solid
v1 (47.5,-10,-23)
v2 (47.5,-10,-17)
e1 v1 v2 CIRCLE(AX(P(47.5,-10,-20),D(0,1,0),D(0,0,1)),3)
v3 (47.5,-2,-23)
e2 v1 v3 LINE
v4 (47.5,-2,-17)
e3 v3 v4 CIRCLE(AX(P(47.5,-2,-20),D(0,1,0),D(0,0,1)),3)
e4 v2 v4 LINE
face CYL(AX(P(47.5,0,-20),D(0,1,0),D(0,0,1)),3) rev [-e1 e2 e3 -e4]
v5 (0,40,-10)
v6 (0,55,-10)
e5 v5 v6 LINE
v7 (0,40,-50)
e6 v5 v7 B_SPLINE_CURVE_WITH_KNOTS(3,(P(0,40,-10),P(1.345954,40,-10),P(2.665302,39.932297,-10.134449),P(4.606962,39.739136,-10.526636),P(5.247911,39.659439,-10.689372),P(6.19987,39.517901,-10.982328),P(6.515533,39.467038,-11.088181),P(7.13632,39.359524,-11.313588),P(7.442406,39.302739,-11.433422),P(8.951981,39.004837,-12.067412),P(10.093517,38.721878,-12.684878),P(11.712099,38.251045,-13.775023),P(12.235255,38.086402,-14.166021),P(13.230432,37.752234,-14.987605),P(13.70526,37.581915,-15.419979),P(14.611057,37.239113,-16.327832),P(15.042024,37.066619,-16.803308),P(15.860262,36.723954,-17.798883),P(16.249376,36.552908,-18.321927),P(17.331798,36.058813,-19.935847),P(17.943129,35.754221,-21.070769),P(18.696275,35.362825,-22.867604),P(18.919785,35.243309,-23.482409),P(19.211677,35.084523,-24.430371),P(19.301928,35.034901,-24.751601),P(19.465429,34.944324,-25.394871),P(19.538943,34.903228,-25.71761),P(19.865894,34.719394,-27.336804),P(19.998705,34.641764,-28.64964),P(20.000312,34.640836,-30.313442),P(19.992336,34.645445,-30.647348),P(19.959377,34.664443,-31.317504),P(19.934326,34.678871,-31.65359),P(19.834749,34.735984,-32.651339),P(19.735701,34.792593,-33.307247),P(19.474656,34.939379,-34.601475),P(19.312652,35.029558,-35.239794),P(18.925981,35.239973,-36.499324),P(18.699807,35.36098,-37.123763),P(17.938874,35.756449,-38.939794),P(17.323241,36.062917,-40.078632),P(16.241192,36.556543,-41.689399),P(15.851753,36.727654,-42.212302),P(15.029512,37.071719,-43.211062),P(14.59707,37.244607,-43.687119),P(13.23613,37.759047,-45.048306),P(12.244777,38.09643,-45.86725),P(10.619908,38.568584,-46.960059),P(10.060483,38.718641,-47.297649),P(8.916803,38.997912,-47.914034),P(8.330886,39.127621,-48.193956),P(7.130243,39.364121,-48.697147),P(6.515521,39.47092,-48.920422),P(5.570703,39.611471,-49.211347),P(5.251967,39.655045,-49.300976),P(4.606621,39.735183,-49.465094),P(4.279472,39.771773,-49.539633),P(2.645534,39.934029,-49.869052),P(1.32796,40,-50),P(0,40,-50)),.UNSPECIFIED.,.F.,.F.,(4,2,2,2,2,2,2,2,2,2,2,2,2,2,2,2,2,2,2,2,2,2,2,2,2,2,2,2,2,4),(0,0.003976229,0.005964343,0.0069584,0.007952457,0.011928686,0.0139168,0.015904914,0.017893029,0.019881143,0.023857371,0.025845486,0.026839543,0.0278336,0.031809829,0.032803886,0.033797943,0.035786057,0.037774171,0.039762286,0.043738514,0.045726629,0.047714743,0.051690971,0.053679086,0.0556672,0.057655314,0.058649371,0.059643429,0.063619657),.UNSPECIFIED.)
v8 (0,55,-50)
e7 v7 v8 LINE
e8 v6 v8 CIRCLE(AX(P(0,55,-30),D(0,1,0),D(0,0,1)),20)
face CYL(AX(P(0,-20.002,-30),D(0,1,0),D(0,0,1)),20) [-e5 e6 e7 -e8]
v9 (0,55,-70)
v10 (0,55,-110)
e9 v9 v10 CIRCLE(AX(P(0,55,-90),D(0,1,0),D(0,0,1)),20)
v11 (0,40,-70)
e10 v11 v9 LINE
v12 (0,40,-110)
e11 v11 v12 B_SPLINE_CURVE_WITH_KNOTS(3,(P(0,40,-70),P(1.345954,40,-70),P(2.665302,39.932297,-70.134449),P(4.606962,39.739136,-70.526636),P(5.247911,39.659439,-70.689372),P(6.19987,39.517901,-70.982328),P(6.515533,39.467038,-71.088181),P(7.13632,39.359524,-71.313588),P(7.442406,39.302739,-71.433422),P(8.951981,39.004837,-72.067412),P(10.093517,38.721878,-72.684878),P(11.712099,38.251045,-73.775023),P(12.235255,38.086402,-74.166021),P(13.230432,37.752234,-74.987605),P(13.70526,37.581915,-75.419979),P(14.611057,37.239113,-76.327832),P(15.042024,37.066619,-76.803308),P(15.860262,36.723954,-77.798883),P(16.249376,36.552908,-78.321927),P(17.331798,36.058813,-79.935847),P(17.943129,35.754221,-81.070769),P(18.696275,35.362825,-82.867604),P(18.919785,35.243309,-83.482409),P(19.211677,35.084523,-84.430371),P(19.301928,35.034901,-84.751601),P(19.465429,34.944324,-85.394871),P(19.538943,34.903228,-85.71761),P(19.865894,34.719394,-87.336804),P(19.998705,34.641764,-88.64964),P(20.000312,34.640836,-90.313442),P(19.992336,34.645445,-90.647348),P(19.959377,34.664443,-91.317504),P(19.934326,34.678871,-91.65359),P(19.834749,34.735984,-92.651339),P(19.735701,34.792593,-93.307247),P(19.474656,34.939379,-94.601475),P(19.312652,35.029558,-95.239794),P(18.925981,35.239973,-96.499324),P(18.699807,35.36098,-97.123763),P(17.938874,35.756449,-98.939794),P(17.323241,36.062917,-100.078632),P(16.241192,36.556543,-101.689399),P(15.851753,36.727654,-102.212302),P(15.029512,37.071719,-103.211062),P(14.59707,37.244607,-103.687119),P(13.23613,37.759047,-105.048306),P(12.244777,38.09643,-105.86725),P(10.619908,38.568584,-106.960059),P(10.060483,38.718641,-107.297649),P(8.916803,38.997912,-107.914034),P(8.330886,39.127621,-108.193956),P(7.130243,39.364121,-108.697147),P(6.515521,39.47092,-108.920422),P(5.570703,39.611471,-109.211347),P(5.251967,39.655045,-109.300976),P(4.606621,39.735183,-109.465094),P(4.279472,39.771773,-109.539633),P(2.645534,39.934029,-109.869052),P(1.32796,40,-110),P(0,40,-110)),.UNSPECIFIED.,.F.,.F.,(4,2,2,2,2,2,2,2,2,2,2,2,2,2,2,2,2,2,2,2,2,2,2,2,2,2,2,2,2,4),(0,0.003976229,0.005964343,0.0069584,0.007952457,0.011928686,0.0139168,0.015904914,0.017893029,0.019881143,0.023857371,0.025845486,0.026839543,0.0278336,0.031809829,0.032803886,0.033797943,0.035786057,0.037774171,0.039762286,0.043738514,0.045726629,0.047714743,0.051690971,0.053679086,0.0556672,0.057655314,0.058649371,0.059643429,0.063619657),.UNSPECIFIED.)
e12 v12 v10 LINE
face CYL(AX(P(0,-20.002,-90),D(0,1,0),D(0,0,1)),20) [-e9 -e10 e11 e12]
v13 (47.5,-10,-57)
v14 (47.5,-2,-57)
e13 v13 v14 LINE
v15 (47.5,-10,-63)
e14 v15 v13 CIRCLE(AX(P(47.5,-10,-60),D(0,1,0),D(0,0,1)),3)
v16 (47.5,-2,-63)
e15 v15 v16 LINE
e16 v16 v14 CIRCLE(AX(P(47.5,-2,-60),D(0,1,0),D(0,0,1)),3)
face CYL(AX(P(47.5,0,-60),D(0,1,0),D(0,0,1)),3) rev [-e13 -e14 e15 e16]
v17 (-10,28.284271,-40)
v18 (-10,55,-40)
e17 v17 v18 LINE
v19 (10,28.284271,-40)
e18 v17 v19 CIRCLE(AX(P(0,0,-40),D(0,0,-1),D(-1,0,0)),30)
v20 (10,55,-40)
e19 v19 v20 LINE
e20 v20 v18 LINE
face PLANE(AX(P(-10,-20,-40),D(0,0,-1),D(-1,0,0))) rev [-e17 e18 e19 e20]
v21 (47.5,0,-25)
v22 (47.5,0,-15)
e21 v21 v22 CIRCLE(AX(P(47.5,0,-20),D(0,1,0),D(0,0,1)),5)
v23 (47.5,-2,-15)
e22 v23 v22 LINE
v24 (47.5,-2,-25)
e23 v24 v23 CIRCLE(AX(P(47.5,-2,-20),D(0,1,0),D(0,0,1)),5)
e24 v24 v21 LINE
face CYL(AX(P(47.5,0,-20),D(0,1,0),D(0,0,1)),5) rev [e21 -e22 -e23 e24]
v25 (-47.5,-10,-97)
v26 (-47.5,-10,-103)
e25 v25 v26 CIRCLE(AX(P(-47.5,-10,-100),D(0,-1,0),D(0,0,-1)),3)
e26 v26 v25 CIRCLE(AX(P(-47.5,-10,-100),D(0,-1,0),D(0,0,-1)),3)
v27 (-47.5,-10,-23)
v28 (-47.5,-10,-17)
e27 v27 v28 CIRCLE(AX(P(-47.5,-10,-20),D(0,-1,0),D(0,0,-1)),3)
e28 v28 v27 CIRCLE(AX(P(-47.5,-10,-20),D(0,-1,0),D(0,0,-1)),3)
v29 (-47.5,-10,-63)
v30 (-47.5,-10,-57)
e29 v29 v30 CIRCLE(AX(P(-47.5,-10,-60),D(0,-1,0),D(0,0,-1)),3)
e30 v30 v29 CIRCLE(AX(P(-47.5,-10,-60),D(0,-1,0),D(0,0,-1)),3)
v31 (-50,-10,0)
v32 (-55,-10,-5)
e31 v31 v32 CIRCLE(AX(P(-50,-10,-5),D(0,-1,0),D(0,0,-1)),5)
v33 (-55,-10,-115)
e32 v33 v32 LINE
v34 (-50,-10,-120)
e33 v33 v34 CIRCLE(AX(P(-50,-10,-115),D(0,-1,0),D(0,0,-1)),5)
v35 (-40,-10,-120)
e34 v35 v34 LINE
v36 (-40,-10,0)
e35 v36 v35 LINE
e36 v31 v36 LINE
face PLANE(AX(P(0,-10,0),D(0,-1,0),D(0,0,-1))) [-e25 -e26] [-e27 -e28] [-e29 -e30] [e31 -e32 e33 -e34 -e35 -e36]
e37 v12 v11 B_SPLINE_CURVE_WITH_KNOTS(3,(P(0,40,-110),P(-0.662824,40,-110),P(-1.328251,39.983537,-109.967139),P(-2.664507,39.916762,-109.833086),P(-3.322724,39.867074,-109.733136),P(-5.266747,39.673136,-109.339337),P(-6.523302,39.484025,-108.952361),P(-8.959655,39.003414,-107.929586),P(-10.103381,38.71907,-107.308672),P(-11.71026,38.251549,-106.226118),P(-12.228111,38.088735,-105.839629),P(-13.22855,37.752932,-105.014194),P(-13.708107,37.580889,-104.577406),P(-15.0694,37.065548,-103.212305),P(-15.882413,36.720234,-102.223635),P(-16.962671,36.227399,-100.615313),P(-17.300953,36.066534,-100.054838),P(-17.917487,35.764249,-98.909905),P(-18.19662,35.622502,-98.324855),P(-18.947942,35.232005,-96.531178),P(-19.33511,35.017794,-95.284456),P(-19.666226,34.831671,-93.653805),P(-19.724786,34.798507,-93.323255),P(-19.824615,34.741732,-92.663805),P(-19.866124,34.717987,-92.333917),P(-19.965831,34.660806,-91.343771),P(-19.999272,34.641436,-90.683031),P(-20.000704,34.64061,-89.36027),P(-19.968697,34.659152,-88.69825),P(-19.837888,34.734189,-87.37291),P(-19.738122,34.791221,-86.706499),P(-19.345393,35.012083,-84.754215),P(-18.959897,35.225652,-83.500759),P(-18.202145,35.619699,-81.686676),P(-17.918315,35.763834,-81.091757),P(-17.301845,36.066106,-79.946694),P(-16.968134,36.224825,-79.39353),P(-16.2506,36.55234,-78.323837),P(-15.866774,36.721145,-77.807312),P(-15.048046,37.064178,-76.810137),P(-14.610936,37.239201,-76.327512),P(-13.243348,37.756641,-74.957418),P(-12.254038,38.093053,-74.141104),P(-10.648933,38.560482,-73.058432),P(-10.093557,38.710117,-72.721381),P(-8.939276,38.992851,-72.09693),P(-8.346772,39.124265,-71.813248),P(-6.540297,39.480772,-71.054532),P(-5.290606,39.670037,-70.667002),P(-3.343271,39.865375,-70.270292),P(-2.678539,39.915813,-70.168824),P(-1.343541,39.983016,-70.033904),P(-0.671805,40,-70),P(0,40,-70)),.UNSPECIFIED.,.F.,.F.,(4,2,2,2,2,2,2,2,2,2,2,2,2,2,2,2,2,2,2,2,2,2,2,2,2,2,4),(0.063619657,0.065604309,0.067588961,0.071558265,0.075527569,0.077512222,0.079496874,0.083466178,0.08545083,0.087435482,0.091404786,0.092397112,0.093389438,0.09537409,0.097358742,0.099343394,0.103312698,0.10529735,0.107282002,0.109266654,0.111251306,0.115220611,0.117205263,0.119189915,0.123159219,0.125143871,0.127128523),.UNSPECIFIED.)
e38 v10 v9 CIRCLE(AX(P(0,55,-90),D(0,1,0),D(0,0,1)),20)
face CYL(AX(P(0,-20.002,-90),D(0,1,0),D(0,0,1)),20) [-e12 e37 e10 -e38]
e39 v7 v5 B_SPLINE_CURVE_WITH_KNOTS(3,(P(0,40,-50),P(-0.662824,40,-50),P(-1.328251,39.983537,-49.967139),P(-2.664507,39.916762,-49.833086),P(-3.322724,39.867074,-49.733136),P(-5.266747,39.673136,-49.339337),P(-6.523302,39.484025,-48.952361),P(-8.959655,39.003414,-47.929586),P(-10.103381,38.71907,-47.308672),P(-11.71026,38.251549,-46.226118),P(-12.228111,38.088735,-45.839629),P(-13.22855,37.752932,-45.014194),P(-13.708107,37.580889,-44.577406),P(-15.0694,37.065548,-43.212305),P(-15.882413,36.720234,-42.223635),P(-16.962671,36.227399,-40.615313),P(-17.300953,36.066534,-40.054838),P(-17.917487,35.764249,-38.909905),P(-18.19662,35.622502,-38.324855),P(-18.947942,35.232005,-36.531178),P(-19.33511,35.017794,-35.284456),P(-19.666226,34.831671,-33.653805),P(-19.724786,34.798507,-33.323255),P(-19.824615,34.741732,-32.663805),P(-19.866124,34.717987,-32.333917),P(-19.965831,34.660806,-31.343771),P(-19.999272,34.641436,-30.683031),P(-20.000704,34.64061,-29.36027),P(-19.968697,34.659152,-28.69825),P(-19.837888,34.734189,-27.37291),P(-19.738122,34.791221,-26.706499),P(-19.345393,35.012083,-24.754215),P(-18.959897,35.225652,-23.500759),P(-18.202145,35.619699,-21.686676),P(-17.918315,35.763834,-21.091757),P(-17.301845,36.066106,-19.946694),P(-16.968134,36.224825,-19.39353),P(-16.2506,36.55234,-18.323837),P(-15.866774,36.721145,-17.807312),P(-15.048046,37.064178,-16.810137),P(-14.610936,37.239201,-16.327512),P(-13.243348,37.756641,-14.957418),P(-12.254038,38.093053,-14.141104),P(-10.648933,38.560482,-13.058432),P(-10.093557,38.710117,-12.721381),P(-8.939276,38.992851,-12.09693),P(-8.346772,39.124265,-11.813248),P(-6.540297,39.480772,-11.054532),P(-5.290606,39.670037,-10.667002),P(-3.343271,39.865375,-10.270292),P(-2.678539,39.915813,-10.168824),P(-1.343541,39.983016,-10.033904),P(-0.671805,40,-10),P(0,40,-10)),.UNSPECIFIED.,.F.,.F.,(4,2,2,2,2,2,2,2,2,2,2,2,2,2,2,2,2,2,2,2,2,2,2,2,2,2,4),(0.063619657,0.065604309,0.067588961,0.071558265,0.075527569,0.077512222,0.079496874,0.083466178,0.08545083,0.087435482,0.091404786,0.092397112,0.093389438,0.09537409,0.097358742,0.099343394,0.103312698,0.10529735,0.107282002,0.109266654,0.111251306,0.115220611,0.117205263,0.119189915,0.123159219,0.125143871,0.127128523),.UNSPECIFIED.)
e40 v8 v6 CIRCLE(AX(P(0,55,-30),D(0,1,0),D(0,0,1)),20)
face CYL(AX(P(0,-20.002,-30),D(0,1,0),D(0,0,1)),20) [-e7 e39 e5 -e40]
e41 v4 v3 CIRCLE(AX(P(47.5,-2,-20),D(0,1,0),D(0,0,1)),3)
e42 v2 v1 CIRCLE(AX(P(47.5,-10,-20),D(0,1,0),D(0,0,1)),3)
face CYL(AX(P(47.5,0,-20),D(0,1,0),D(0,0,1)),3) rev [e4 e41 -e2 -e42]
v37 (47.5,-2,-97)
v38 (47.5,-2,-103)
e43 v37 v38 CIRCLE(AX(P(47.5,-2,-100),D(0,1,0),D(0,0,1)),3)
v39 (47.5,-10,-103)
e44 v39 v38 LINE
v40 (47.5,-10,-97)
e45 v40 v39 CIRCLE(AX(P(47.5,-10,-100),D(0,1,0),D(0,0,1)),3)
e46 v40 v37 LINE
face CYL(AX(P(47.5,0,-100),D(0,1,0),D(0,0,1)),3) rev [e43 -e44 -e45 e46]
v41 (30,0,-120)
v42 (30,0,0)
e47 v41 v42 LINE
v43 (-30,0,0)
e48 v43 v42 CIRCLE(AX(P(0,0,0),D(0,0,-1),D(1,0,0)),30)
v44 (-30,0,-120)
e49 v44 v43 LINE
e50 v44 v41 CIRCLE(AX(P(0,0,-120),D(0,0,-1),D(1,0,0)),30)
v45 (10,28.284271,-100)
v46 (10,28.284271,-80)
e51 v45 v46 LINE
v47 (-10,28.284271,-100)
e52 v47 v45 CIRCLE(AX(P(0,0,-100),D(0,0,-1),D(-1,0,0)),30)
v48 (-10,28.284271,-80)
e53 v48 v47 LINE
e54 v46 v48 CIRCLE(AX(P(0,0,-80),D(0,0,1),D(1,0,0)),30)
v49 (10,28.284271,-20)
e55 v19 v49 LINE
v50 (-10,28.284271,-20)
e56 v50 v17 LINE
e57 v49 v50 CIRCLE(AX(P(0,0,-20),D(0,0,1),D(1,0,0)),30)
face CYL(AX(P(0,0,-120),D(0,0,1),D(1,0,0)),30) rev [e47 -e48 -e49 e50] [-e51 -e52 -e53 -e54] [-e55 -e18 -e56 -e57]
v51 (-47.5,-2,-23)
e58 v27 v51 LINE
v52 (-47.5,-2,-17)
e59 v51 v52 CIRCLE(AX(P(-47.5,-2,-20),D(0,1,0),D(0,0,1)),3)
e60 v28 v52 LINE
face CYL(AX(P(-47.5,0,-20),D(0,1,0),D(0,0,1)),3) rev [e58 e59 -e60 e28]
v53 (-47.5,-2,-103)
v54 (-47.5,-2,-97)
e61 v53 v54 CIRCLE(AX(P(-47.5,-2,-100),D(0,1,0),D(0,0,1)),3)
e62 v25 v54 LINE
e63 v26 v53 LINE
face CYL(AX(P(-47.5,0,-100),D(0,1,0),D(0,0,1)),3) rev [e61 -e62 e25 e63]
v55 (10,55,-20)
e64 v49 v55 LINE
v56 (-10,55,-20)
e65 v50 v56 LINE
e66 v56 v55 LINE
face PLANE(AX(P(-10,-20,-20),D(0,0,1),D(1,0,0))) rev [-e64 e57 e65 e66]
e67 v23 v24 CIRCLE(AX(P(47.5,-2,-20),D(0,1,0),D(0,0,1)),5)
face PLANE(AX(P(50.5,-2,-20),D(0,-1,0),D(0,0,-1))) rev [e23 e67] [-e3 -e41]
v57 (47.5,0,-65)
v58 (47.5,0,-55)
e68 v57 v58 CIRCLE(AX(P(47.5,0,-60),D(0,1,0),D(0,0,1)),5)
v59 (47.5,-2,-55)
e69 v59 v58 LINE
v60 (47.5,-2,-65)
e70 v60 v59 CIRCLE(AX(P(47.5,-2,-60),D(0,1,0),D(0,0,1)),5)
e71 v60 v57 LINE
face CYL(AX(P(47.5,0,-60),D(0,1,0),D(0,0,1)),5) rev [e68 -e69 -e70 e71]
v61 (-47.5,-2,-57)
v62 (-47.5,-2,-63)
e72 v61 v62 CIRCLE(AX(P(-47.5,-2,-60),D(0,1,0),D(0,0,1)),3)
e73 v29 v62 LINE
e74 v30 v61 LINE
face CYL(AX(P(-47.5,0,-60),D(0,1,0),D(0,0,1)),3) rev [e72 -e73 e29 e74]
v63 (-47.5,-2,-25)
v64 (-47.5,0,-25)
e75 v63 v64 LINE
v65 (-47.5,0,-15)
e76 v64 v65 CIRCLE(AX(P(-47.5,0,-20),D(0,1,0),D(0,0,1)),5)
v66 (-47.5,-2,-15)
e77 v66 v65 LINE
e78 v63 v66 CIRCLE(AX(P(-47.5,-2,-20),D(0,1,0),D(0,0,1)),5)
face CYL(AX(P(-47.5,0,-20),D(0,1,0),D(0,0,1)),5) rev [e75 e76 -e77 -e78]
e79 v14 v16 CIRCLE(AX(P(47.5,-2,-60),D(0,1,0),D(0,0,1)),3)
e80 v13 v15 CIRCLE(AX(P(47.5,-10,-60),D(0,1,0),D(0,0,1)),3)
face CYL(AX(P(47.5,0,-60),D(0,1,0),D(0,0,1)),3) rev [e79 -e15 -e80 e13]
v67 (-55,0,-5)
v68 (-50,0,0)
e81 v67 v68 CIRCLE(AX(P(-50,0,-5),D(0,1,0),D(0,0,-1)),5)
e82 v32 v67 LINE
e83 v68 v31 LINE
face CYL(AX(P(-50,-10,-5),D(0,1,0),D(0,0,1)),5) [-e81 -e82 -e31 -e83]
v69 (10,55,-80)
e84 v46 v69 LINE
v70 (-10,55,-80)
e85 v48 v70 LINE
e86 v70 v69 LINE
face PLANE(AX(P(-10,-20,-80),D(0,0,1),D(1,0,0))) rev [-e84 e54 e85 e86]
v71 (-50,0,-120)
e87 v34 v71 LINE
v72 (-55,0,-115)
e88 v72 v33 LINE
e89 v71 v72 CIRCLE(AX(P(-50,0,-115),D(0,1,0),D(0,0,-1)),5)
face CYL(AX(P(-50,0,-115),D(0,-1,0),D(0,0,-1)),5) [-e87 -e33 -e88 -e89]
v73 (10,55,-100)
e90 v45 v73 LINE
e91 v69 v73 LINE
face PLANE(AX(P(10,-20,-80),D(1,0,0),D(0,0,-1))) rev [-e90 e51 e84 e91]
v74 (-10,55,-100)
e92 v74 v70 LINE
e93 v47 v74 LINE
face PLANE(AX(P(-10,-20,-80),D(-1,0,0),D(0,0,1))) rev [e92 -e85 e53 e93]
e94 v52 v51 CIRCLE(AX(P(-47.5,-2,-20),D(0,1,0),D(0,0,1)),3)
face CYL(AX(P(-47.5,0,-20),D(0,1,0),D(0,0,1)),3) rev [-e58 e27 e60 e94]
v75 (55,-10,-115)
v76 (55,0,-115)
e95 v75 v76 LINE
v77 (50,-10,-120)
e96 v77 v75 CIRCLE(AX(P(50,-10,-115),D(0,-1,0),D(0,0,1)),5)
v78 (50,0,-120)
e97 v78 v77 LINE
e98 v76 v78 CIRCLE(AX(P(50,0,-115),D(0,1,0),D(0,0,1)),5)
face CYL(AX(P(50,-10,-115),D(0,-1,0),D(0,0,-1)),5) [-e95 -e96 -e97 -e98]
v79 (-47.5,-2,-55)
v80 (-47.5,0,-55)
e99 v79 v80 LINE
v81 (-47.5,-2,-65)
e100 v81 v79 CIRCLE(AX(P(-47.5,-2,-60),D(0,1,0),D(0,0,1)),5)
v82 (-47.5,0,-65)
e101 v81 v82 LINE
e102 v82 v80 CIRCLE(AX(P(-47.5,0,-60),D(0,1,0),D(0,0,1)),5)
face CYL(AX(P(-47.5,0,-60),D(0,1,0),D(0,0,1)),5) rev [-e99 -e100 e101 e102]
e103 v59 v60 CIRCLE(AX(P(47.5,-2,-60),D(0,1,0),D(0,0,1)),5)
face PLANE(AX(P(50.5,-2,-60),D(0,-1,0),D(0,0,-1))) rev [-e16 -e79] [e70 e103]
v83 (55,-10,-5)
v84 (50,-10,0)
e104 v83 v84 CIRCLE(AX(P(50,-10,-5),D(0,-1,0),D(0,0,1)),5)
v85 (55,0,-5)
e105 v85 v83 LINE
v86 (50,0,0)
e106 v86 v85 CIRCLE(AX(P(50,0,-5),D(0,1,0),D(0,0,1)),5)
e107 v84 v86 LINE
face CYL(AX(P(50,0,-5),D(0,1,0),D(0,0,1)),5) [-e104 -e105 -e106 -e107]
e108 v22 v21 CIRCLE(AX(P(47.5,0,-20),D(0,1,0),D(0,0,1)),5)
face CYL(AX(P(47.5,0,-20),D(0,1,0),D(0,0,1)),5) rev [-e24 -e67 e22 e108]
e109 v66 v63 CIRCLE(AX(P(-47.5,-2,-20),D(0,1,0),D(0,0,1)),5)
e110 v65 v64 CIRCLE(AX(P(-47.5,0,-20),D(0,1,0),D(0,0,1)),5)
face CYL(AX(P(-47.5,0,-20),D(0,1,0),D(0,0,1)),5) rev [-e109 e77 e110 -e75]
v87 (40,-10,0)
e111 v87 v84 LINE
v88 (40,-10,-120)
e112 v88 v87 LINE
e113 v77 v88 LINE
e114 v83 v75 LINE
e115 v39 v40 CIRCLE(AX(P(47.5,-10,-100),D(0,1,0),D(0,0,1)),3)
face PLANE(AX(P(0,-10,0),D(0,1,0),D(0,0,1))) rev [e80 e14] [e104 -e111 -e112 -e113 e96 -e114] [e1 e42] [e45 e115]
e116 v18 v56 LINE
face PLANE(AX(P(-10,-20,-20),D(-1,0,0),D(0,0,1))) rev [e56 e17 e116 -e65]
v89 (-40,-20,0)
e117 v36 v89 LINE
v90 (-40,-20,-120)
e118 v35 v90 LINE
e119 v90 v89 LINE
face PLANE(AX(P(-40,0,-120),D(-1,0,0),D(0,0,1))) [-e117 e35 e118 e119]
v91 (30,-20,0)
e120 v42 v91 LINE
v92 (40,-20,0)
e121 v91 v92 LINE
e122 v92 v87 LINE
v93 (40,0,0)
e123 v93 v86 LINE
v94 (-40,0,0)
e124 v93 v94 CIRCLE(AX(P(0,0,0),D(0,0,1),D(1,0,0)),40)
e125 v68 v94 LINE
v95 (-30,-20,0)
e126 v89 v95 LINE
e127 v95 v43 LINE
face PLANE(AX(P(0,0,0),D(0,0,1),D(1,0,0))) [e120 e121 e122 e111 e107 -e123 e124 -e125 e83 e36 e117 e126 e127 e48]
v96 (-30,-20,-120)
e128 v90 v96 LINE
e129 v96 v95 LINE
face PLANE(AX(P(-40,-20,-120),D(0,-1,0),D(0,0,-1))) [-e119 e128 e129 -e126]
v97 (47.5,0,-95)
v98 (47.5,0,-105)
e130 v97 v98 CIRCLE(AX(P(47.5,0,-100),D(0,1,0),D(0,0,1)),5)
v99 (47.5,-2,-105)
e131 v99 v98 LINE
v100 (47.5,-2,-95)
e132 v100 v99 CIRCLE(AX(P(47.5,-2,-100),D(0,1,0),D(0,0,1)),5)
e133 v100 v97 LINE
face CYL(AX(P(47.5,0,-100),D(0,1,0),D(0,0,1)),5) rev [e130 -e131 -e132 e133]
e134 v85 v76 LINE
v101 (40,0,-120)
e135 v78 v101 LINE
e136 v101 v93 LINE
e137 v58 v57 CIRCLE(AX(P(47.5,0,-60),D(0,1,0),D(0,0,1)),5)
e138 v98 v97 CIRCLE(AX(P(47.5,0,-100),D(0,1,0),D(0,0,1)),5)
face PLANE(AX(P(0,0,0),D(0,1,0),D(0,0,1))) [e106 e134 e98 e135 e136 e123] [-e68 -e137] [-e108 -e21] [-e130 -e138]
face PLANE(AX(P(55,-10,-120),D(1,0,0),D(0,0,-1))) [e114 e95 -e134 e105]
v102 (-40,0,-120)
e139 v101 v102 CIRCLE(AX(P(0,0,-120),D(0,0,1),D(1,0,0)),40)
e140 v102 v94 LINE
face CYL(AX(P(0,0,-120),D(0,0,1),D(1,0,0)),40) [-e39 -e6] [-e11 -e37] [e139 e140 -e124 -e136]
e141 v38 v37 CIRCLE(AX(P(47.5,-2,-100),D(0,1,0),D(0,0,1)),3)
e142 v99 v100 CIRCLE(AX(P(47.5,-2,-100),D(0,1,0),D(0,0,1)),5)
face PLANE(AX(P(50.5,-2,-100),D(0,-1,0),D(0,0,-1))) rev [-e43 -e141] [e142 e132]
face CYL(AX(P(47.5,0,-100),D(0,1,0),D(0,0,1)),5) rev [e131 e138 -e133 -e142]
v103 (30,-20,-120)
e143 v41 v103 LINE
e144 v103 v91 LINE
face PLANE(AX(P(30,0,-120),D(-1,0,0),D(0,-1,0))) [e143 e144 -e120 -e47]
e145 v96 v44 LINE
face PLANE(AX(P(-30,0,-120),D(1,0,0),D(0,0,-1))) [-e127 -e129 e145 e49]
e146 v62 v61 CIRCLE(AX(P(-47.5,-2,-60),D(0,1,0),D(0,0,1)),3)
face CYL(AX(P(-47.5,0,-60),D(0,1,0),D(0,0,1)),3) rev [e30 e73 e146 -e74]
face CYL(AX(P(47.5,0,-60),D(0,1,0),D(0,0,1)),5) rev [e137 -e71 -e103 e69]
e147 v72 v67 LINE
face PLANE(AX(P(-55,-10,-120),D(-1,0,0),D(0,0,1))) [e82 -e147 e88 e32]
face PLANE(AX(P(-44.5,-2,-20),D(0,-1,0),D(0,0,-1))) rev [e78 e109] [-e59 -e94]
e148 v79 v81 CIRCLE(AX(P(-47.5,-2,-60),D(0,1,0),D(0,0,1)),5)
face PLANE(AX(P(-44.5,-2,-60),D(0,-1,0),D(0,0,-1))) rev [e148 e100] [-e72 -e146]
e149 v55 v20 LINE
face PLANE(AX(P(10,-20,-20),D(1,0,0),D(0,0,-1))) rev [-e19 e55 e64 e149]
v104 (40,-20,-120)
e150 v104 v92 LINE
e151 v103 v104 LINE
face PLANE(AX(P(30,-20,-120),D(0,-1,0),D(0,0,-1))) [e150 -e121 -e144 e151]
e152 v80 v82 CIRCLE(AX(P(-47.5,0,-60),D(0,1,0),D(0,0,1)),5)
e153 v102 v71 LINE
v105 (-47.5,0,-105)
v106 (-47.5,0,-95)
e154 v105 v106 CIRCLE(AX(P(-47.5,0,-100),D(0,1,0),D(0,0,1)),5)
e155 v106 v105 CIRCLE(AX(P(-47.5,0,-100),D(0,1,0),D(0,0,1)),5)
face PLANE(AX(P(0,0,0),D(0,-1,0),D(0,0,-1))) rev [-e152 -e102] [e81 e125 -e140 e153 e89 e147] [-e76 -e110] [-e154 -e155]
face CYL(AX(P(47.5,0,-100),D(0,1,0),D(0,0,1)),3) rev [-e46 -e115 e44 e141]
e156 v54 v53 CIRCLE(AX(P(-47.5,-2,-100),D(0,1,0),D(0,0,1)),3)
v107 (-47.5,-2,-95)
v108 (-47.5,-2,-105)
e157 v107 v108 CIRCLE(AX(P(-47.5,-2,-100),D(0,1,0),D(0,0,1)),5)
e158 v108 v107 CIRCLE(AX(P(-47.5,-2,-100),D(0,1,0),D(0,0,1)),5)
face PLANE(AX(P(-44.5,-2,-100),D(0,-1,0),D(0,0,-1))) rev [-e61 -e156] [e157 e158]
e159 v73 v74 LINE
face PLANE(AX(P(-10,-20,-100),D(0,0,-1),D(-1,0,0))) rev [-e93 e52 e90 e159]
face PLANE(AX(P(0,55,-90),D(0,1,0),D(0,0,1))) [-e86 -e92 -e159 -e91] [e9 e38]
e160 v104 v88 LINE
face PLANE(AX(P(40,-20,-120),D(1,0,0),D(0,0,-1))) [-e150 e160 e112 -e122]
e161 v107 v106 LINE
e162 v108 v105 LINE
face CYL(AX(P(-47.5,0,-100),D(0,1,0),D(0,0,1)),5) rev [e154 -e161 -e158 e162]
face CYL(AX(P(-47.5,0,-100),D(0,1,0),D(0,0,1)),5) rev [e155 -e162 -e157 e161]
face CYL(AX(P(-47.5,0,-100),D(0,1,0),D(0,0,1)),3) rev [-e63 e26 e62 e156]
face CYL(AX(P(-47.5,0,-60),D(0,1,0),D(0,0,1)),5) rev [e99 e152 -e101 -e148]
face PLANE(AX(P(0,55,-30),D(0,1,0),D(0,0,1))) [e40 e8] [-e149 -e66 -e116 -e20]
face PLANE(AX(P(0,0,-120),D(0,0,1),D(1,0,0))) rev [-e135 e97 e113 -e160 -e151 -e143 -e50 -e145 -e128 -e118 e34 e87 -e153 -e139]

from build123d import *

# Parameters (mm, degrees)
SADDLE_BODY_DEPTH                       = 120
FLANGE_SKETCH_W                         = 15
FLANGE_SKETCH_H                         = 120
MOUNTING_FLANGE_DEPTH                   = 10
COUNTERBORED_FLANGE_HOLES_6_D           = 6
COUNTERBORED_FLANGE_HOLES_6_DEPTH       = 11.832159566
COUNTERBORED_FLANGE_HOLES_6_CBORE_D     = 10
COUNTERBORED_FLANGE_HOLES_6_CBORE_DEPTH = 2
TWIN_BOSSES_REACH                       = 153.822
TWIN_BOSSES_END_RADIUS                  = 40
TWIN_BOSS_SKETCH_R                      = 20
SQUARE_SOCKET_SKETCH_W                  = 20
SQUARE_SOCKET_SKETCH_H                  = 20
SQUARE_SOCKETS_20X20_DEPTH              = 152.822264586
FLANGE_FILLET_R5_R                      = 5


with BuildPart() as part:
    # Saddle Profile Sketch → Saddle Body (new body)
    with BuildSketch(Plane.XY):
        with BuildLine():
            Line((-40, 0), (-40, -20))
            Line((-40, -20), (-30, -20))
            Line((-30, -20), (-30, 0))
            ThreePointArc((-30, 0), (0, 30), (30, 0))
            Line((30, 0), (30, -20))
            Line((30, -20), (40, -20))
            Line((40, -20), (40, 0))
            ThreePointArc((40, 0), (0, 40), (-40, 0))
        make_face()
    extrude(amount=-SADDLE_BODY_DEPTH)

    # Flange Sketch → Mounting Flange (add)
    with BuildSketch(Plane(origin=(0, 0, 0), x_dir=(1, 0, 0), z_dir=(0, 1, 0))):
        with Locations((47.5, 60)):
            Rectangle(FLANGE_SKETCH_W, FLANGE_SKETCH_H)
        with Locations((-47.5, 60)):
            Rectangle(FLANGE_SKETCH_W, FLANGE_SKETCH_H)
    extrude(amount=-MOUNTING_FLANGE_DEPTH)

    # Counterbored Flange Holes Ø6
    with Locations(Plane(origin=(0, 0, 0), x_dir=(1, 0, 0), z_dir=(0, 1, 0))):
        with Locations((-47.5, 100), (-47.5, 60), (-47.5, 20), (47.5, 20), (47.5, 60), (47.5, 100)):
            CounterBoreHole(COUNTERBORED_FLANGE_HOLES_6_D / 2, COUNTERBORED_FLANGE_HOLES_6_CBORE_D / 2, COUNTERBORED_FLANGE_HOLES_6_CBORE_DEPTH, depth=COUNTERBORED_FLANGE_HOLES_6_DEPTH)

    # Twin Bosses: up to this cylinder (the profile starts outside it)
    twin_bosses_end = Plane(origin=(0, 0, -60), z_dir=(0, 0, 1)) * Cylinder(TWIN_BOSSES_END_RADIUS, 448.644, mode=Mode.PRIVATE)
    # Twin Boss Sketch → Twin Bosses (add, up to the surface)
    with BuildSketch(Plane(origin=(0, 55, 0), x_dir=(1, 0, 0), z_dir=(0, 1, 0)), mode=Mode.PRIVATE) as twin_bosses_sk1:
        with Locations(Location((0, 90, 0), (0, 0, 270))):
            Circle(TWIN_BOSS_SKETCH_R)
    twin_bosses_tool1 = extrude(twin_bosses_sk1.sketch, amount=-TWIN_BOSSES_REACH, mode=Mode.PRIVATE) - twin_bosses_end
    add(twin_bosses_tool1.solids().sort_by_distance((0, 55, -90))[0])
    # Twin Boss Sketch → Twin Bosses (add, up to the surface)
    with BuildSketch(Plane(origin=(0, 55, 0), x_dir=(1, 0, 0), z_dir=(0, 1, 0)), mode=Mode.PRIVATE) as twin_bosses_sk2:
        with Locations(Location((0, 30, 0), (0, 0, 270))):
            Circle(TWIN_BOSS_SKETCH_R)
    twin_bosses_tool2 = extrude(twin_bosses_sk2.sketch, amount=-TWIN_BOSSES_REACH, mode=Mode.PRIVATE) - twin_bosses_end
    add(twin_bosses_tool2.solids().sort_by_distance((0, 55, -30))[0])

    # Square Socket Sketch → Square Sockets 20x20 (cut, through all)
    with BuildSketch(Plane(origin=(0, 55, 0), x_dir=(1, 0, 0), z_dir=(0, 1, 0))):
        with Locations((0, 90)):
            Rectangle(SQUARE_SOCKET_SKETCH_W, SQUARE_SOCKET_SKETCH_H)
        with Locations((0, 30)):
            Rectangle(SQUARE_SOCKET_SKETCH_W, SQUARE_SOCKET_SKETCH_H)
    extrude(amount=-SQUARE_SOCKETS_20X20_DEPTH, mode=Mode.SUBTRACT)

    # Flange Fillet R5
    flange_fillet_r5_edges = [part.edges().sort_by_distance(p)[0] for p in [
        (55, -5, -120),
        (55, -5, 0),
        (-55, -5, 0),
        (-55, -5, -120),
    ]]
    fillet(flange_fillet_r5_edges, radius=FLANGE_FILLET_R5_R)


solid = part.part
